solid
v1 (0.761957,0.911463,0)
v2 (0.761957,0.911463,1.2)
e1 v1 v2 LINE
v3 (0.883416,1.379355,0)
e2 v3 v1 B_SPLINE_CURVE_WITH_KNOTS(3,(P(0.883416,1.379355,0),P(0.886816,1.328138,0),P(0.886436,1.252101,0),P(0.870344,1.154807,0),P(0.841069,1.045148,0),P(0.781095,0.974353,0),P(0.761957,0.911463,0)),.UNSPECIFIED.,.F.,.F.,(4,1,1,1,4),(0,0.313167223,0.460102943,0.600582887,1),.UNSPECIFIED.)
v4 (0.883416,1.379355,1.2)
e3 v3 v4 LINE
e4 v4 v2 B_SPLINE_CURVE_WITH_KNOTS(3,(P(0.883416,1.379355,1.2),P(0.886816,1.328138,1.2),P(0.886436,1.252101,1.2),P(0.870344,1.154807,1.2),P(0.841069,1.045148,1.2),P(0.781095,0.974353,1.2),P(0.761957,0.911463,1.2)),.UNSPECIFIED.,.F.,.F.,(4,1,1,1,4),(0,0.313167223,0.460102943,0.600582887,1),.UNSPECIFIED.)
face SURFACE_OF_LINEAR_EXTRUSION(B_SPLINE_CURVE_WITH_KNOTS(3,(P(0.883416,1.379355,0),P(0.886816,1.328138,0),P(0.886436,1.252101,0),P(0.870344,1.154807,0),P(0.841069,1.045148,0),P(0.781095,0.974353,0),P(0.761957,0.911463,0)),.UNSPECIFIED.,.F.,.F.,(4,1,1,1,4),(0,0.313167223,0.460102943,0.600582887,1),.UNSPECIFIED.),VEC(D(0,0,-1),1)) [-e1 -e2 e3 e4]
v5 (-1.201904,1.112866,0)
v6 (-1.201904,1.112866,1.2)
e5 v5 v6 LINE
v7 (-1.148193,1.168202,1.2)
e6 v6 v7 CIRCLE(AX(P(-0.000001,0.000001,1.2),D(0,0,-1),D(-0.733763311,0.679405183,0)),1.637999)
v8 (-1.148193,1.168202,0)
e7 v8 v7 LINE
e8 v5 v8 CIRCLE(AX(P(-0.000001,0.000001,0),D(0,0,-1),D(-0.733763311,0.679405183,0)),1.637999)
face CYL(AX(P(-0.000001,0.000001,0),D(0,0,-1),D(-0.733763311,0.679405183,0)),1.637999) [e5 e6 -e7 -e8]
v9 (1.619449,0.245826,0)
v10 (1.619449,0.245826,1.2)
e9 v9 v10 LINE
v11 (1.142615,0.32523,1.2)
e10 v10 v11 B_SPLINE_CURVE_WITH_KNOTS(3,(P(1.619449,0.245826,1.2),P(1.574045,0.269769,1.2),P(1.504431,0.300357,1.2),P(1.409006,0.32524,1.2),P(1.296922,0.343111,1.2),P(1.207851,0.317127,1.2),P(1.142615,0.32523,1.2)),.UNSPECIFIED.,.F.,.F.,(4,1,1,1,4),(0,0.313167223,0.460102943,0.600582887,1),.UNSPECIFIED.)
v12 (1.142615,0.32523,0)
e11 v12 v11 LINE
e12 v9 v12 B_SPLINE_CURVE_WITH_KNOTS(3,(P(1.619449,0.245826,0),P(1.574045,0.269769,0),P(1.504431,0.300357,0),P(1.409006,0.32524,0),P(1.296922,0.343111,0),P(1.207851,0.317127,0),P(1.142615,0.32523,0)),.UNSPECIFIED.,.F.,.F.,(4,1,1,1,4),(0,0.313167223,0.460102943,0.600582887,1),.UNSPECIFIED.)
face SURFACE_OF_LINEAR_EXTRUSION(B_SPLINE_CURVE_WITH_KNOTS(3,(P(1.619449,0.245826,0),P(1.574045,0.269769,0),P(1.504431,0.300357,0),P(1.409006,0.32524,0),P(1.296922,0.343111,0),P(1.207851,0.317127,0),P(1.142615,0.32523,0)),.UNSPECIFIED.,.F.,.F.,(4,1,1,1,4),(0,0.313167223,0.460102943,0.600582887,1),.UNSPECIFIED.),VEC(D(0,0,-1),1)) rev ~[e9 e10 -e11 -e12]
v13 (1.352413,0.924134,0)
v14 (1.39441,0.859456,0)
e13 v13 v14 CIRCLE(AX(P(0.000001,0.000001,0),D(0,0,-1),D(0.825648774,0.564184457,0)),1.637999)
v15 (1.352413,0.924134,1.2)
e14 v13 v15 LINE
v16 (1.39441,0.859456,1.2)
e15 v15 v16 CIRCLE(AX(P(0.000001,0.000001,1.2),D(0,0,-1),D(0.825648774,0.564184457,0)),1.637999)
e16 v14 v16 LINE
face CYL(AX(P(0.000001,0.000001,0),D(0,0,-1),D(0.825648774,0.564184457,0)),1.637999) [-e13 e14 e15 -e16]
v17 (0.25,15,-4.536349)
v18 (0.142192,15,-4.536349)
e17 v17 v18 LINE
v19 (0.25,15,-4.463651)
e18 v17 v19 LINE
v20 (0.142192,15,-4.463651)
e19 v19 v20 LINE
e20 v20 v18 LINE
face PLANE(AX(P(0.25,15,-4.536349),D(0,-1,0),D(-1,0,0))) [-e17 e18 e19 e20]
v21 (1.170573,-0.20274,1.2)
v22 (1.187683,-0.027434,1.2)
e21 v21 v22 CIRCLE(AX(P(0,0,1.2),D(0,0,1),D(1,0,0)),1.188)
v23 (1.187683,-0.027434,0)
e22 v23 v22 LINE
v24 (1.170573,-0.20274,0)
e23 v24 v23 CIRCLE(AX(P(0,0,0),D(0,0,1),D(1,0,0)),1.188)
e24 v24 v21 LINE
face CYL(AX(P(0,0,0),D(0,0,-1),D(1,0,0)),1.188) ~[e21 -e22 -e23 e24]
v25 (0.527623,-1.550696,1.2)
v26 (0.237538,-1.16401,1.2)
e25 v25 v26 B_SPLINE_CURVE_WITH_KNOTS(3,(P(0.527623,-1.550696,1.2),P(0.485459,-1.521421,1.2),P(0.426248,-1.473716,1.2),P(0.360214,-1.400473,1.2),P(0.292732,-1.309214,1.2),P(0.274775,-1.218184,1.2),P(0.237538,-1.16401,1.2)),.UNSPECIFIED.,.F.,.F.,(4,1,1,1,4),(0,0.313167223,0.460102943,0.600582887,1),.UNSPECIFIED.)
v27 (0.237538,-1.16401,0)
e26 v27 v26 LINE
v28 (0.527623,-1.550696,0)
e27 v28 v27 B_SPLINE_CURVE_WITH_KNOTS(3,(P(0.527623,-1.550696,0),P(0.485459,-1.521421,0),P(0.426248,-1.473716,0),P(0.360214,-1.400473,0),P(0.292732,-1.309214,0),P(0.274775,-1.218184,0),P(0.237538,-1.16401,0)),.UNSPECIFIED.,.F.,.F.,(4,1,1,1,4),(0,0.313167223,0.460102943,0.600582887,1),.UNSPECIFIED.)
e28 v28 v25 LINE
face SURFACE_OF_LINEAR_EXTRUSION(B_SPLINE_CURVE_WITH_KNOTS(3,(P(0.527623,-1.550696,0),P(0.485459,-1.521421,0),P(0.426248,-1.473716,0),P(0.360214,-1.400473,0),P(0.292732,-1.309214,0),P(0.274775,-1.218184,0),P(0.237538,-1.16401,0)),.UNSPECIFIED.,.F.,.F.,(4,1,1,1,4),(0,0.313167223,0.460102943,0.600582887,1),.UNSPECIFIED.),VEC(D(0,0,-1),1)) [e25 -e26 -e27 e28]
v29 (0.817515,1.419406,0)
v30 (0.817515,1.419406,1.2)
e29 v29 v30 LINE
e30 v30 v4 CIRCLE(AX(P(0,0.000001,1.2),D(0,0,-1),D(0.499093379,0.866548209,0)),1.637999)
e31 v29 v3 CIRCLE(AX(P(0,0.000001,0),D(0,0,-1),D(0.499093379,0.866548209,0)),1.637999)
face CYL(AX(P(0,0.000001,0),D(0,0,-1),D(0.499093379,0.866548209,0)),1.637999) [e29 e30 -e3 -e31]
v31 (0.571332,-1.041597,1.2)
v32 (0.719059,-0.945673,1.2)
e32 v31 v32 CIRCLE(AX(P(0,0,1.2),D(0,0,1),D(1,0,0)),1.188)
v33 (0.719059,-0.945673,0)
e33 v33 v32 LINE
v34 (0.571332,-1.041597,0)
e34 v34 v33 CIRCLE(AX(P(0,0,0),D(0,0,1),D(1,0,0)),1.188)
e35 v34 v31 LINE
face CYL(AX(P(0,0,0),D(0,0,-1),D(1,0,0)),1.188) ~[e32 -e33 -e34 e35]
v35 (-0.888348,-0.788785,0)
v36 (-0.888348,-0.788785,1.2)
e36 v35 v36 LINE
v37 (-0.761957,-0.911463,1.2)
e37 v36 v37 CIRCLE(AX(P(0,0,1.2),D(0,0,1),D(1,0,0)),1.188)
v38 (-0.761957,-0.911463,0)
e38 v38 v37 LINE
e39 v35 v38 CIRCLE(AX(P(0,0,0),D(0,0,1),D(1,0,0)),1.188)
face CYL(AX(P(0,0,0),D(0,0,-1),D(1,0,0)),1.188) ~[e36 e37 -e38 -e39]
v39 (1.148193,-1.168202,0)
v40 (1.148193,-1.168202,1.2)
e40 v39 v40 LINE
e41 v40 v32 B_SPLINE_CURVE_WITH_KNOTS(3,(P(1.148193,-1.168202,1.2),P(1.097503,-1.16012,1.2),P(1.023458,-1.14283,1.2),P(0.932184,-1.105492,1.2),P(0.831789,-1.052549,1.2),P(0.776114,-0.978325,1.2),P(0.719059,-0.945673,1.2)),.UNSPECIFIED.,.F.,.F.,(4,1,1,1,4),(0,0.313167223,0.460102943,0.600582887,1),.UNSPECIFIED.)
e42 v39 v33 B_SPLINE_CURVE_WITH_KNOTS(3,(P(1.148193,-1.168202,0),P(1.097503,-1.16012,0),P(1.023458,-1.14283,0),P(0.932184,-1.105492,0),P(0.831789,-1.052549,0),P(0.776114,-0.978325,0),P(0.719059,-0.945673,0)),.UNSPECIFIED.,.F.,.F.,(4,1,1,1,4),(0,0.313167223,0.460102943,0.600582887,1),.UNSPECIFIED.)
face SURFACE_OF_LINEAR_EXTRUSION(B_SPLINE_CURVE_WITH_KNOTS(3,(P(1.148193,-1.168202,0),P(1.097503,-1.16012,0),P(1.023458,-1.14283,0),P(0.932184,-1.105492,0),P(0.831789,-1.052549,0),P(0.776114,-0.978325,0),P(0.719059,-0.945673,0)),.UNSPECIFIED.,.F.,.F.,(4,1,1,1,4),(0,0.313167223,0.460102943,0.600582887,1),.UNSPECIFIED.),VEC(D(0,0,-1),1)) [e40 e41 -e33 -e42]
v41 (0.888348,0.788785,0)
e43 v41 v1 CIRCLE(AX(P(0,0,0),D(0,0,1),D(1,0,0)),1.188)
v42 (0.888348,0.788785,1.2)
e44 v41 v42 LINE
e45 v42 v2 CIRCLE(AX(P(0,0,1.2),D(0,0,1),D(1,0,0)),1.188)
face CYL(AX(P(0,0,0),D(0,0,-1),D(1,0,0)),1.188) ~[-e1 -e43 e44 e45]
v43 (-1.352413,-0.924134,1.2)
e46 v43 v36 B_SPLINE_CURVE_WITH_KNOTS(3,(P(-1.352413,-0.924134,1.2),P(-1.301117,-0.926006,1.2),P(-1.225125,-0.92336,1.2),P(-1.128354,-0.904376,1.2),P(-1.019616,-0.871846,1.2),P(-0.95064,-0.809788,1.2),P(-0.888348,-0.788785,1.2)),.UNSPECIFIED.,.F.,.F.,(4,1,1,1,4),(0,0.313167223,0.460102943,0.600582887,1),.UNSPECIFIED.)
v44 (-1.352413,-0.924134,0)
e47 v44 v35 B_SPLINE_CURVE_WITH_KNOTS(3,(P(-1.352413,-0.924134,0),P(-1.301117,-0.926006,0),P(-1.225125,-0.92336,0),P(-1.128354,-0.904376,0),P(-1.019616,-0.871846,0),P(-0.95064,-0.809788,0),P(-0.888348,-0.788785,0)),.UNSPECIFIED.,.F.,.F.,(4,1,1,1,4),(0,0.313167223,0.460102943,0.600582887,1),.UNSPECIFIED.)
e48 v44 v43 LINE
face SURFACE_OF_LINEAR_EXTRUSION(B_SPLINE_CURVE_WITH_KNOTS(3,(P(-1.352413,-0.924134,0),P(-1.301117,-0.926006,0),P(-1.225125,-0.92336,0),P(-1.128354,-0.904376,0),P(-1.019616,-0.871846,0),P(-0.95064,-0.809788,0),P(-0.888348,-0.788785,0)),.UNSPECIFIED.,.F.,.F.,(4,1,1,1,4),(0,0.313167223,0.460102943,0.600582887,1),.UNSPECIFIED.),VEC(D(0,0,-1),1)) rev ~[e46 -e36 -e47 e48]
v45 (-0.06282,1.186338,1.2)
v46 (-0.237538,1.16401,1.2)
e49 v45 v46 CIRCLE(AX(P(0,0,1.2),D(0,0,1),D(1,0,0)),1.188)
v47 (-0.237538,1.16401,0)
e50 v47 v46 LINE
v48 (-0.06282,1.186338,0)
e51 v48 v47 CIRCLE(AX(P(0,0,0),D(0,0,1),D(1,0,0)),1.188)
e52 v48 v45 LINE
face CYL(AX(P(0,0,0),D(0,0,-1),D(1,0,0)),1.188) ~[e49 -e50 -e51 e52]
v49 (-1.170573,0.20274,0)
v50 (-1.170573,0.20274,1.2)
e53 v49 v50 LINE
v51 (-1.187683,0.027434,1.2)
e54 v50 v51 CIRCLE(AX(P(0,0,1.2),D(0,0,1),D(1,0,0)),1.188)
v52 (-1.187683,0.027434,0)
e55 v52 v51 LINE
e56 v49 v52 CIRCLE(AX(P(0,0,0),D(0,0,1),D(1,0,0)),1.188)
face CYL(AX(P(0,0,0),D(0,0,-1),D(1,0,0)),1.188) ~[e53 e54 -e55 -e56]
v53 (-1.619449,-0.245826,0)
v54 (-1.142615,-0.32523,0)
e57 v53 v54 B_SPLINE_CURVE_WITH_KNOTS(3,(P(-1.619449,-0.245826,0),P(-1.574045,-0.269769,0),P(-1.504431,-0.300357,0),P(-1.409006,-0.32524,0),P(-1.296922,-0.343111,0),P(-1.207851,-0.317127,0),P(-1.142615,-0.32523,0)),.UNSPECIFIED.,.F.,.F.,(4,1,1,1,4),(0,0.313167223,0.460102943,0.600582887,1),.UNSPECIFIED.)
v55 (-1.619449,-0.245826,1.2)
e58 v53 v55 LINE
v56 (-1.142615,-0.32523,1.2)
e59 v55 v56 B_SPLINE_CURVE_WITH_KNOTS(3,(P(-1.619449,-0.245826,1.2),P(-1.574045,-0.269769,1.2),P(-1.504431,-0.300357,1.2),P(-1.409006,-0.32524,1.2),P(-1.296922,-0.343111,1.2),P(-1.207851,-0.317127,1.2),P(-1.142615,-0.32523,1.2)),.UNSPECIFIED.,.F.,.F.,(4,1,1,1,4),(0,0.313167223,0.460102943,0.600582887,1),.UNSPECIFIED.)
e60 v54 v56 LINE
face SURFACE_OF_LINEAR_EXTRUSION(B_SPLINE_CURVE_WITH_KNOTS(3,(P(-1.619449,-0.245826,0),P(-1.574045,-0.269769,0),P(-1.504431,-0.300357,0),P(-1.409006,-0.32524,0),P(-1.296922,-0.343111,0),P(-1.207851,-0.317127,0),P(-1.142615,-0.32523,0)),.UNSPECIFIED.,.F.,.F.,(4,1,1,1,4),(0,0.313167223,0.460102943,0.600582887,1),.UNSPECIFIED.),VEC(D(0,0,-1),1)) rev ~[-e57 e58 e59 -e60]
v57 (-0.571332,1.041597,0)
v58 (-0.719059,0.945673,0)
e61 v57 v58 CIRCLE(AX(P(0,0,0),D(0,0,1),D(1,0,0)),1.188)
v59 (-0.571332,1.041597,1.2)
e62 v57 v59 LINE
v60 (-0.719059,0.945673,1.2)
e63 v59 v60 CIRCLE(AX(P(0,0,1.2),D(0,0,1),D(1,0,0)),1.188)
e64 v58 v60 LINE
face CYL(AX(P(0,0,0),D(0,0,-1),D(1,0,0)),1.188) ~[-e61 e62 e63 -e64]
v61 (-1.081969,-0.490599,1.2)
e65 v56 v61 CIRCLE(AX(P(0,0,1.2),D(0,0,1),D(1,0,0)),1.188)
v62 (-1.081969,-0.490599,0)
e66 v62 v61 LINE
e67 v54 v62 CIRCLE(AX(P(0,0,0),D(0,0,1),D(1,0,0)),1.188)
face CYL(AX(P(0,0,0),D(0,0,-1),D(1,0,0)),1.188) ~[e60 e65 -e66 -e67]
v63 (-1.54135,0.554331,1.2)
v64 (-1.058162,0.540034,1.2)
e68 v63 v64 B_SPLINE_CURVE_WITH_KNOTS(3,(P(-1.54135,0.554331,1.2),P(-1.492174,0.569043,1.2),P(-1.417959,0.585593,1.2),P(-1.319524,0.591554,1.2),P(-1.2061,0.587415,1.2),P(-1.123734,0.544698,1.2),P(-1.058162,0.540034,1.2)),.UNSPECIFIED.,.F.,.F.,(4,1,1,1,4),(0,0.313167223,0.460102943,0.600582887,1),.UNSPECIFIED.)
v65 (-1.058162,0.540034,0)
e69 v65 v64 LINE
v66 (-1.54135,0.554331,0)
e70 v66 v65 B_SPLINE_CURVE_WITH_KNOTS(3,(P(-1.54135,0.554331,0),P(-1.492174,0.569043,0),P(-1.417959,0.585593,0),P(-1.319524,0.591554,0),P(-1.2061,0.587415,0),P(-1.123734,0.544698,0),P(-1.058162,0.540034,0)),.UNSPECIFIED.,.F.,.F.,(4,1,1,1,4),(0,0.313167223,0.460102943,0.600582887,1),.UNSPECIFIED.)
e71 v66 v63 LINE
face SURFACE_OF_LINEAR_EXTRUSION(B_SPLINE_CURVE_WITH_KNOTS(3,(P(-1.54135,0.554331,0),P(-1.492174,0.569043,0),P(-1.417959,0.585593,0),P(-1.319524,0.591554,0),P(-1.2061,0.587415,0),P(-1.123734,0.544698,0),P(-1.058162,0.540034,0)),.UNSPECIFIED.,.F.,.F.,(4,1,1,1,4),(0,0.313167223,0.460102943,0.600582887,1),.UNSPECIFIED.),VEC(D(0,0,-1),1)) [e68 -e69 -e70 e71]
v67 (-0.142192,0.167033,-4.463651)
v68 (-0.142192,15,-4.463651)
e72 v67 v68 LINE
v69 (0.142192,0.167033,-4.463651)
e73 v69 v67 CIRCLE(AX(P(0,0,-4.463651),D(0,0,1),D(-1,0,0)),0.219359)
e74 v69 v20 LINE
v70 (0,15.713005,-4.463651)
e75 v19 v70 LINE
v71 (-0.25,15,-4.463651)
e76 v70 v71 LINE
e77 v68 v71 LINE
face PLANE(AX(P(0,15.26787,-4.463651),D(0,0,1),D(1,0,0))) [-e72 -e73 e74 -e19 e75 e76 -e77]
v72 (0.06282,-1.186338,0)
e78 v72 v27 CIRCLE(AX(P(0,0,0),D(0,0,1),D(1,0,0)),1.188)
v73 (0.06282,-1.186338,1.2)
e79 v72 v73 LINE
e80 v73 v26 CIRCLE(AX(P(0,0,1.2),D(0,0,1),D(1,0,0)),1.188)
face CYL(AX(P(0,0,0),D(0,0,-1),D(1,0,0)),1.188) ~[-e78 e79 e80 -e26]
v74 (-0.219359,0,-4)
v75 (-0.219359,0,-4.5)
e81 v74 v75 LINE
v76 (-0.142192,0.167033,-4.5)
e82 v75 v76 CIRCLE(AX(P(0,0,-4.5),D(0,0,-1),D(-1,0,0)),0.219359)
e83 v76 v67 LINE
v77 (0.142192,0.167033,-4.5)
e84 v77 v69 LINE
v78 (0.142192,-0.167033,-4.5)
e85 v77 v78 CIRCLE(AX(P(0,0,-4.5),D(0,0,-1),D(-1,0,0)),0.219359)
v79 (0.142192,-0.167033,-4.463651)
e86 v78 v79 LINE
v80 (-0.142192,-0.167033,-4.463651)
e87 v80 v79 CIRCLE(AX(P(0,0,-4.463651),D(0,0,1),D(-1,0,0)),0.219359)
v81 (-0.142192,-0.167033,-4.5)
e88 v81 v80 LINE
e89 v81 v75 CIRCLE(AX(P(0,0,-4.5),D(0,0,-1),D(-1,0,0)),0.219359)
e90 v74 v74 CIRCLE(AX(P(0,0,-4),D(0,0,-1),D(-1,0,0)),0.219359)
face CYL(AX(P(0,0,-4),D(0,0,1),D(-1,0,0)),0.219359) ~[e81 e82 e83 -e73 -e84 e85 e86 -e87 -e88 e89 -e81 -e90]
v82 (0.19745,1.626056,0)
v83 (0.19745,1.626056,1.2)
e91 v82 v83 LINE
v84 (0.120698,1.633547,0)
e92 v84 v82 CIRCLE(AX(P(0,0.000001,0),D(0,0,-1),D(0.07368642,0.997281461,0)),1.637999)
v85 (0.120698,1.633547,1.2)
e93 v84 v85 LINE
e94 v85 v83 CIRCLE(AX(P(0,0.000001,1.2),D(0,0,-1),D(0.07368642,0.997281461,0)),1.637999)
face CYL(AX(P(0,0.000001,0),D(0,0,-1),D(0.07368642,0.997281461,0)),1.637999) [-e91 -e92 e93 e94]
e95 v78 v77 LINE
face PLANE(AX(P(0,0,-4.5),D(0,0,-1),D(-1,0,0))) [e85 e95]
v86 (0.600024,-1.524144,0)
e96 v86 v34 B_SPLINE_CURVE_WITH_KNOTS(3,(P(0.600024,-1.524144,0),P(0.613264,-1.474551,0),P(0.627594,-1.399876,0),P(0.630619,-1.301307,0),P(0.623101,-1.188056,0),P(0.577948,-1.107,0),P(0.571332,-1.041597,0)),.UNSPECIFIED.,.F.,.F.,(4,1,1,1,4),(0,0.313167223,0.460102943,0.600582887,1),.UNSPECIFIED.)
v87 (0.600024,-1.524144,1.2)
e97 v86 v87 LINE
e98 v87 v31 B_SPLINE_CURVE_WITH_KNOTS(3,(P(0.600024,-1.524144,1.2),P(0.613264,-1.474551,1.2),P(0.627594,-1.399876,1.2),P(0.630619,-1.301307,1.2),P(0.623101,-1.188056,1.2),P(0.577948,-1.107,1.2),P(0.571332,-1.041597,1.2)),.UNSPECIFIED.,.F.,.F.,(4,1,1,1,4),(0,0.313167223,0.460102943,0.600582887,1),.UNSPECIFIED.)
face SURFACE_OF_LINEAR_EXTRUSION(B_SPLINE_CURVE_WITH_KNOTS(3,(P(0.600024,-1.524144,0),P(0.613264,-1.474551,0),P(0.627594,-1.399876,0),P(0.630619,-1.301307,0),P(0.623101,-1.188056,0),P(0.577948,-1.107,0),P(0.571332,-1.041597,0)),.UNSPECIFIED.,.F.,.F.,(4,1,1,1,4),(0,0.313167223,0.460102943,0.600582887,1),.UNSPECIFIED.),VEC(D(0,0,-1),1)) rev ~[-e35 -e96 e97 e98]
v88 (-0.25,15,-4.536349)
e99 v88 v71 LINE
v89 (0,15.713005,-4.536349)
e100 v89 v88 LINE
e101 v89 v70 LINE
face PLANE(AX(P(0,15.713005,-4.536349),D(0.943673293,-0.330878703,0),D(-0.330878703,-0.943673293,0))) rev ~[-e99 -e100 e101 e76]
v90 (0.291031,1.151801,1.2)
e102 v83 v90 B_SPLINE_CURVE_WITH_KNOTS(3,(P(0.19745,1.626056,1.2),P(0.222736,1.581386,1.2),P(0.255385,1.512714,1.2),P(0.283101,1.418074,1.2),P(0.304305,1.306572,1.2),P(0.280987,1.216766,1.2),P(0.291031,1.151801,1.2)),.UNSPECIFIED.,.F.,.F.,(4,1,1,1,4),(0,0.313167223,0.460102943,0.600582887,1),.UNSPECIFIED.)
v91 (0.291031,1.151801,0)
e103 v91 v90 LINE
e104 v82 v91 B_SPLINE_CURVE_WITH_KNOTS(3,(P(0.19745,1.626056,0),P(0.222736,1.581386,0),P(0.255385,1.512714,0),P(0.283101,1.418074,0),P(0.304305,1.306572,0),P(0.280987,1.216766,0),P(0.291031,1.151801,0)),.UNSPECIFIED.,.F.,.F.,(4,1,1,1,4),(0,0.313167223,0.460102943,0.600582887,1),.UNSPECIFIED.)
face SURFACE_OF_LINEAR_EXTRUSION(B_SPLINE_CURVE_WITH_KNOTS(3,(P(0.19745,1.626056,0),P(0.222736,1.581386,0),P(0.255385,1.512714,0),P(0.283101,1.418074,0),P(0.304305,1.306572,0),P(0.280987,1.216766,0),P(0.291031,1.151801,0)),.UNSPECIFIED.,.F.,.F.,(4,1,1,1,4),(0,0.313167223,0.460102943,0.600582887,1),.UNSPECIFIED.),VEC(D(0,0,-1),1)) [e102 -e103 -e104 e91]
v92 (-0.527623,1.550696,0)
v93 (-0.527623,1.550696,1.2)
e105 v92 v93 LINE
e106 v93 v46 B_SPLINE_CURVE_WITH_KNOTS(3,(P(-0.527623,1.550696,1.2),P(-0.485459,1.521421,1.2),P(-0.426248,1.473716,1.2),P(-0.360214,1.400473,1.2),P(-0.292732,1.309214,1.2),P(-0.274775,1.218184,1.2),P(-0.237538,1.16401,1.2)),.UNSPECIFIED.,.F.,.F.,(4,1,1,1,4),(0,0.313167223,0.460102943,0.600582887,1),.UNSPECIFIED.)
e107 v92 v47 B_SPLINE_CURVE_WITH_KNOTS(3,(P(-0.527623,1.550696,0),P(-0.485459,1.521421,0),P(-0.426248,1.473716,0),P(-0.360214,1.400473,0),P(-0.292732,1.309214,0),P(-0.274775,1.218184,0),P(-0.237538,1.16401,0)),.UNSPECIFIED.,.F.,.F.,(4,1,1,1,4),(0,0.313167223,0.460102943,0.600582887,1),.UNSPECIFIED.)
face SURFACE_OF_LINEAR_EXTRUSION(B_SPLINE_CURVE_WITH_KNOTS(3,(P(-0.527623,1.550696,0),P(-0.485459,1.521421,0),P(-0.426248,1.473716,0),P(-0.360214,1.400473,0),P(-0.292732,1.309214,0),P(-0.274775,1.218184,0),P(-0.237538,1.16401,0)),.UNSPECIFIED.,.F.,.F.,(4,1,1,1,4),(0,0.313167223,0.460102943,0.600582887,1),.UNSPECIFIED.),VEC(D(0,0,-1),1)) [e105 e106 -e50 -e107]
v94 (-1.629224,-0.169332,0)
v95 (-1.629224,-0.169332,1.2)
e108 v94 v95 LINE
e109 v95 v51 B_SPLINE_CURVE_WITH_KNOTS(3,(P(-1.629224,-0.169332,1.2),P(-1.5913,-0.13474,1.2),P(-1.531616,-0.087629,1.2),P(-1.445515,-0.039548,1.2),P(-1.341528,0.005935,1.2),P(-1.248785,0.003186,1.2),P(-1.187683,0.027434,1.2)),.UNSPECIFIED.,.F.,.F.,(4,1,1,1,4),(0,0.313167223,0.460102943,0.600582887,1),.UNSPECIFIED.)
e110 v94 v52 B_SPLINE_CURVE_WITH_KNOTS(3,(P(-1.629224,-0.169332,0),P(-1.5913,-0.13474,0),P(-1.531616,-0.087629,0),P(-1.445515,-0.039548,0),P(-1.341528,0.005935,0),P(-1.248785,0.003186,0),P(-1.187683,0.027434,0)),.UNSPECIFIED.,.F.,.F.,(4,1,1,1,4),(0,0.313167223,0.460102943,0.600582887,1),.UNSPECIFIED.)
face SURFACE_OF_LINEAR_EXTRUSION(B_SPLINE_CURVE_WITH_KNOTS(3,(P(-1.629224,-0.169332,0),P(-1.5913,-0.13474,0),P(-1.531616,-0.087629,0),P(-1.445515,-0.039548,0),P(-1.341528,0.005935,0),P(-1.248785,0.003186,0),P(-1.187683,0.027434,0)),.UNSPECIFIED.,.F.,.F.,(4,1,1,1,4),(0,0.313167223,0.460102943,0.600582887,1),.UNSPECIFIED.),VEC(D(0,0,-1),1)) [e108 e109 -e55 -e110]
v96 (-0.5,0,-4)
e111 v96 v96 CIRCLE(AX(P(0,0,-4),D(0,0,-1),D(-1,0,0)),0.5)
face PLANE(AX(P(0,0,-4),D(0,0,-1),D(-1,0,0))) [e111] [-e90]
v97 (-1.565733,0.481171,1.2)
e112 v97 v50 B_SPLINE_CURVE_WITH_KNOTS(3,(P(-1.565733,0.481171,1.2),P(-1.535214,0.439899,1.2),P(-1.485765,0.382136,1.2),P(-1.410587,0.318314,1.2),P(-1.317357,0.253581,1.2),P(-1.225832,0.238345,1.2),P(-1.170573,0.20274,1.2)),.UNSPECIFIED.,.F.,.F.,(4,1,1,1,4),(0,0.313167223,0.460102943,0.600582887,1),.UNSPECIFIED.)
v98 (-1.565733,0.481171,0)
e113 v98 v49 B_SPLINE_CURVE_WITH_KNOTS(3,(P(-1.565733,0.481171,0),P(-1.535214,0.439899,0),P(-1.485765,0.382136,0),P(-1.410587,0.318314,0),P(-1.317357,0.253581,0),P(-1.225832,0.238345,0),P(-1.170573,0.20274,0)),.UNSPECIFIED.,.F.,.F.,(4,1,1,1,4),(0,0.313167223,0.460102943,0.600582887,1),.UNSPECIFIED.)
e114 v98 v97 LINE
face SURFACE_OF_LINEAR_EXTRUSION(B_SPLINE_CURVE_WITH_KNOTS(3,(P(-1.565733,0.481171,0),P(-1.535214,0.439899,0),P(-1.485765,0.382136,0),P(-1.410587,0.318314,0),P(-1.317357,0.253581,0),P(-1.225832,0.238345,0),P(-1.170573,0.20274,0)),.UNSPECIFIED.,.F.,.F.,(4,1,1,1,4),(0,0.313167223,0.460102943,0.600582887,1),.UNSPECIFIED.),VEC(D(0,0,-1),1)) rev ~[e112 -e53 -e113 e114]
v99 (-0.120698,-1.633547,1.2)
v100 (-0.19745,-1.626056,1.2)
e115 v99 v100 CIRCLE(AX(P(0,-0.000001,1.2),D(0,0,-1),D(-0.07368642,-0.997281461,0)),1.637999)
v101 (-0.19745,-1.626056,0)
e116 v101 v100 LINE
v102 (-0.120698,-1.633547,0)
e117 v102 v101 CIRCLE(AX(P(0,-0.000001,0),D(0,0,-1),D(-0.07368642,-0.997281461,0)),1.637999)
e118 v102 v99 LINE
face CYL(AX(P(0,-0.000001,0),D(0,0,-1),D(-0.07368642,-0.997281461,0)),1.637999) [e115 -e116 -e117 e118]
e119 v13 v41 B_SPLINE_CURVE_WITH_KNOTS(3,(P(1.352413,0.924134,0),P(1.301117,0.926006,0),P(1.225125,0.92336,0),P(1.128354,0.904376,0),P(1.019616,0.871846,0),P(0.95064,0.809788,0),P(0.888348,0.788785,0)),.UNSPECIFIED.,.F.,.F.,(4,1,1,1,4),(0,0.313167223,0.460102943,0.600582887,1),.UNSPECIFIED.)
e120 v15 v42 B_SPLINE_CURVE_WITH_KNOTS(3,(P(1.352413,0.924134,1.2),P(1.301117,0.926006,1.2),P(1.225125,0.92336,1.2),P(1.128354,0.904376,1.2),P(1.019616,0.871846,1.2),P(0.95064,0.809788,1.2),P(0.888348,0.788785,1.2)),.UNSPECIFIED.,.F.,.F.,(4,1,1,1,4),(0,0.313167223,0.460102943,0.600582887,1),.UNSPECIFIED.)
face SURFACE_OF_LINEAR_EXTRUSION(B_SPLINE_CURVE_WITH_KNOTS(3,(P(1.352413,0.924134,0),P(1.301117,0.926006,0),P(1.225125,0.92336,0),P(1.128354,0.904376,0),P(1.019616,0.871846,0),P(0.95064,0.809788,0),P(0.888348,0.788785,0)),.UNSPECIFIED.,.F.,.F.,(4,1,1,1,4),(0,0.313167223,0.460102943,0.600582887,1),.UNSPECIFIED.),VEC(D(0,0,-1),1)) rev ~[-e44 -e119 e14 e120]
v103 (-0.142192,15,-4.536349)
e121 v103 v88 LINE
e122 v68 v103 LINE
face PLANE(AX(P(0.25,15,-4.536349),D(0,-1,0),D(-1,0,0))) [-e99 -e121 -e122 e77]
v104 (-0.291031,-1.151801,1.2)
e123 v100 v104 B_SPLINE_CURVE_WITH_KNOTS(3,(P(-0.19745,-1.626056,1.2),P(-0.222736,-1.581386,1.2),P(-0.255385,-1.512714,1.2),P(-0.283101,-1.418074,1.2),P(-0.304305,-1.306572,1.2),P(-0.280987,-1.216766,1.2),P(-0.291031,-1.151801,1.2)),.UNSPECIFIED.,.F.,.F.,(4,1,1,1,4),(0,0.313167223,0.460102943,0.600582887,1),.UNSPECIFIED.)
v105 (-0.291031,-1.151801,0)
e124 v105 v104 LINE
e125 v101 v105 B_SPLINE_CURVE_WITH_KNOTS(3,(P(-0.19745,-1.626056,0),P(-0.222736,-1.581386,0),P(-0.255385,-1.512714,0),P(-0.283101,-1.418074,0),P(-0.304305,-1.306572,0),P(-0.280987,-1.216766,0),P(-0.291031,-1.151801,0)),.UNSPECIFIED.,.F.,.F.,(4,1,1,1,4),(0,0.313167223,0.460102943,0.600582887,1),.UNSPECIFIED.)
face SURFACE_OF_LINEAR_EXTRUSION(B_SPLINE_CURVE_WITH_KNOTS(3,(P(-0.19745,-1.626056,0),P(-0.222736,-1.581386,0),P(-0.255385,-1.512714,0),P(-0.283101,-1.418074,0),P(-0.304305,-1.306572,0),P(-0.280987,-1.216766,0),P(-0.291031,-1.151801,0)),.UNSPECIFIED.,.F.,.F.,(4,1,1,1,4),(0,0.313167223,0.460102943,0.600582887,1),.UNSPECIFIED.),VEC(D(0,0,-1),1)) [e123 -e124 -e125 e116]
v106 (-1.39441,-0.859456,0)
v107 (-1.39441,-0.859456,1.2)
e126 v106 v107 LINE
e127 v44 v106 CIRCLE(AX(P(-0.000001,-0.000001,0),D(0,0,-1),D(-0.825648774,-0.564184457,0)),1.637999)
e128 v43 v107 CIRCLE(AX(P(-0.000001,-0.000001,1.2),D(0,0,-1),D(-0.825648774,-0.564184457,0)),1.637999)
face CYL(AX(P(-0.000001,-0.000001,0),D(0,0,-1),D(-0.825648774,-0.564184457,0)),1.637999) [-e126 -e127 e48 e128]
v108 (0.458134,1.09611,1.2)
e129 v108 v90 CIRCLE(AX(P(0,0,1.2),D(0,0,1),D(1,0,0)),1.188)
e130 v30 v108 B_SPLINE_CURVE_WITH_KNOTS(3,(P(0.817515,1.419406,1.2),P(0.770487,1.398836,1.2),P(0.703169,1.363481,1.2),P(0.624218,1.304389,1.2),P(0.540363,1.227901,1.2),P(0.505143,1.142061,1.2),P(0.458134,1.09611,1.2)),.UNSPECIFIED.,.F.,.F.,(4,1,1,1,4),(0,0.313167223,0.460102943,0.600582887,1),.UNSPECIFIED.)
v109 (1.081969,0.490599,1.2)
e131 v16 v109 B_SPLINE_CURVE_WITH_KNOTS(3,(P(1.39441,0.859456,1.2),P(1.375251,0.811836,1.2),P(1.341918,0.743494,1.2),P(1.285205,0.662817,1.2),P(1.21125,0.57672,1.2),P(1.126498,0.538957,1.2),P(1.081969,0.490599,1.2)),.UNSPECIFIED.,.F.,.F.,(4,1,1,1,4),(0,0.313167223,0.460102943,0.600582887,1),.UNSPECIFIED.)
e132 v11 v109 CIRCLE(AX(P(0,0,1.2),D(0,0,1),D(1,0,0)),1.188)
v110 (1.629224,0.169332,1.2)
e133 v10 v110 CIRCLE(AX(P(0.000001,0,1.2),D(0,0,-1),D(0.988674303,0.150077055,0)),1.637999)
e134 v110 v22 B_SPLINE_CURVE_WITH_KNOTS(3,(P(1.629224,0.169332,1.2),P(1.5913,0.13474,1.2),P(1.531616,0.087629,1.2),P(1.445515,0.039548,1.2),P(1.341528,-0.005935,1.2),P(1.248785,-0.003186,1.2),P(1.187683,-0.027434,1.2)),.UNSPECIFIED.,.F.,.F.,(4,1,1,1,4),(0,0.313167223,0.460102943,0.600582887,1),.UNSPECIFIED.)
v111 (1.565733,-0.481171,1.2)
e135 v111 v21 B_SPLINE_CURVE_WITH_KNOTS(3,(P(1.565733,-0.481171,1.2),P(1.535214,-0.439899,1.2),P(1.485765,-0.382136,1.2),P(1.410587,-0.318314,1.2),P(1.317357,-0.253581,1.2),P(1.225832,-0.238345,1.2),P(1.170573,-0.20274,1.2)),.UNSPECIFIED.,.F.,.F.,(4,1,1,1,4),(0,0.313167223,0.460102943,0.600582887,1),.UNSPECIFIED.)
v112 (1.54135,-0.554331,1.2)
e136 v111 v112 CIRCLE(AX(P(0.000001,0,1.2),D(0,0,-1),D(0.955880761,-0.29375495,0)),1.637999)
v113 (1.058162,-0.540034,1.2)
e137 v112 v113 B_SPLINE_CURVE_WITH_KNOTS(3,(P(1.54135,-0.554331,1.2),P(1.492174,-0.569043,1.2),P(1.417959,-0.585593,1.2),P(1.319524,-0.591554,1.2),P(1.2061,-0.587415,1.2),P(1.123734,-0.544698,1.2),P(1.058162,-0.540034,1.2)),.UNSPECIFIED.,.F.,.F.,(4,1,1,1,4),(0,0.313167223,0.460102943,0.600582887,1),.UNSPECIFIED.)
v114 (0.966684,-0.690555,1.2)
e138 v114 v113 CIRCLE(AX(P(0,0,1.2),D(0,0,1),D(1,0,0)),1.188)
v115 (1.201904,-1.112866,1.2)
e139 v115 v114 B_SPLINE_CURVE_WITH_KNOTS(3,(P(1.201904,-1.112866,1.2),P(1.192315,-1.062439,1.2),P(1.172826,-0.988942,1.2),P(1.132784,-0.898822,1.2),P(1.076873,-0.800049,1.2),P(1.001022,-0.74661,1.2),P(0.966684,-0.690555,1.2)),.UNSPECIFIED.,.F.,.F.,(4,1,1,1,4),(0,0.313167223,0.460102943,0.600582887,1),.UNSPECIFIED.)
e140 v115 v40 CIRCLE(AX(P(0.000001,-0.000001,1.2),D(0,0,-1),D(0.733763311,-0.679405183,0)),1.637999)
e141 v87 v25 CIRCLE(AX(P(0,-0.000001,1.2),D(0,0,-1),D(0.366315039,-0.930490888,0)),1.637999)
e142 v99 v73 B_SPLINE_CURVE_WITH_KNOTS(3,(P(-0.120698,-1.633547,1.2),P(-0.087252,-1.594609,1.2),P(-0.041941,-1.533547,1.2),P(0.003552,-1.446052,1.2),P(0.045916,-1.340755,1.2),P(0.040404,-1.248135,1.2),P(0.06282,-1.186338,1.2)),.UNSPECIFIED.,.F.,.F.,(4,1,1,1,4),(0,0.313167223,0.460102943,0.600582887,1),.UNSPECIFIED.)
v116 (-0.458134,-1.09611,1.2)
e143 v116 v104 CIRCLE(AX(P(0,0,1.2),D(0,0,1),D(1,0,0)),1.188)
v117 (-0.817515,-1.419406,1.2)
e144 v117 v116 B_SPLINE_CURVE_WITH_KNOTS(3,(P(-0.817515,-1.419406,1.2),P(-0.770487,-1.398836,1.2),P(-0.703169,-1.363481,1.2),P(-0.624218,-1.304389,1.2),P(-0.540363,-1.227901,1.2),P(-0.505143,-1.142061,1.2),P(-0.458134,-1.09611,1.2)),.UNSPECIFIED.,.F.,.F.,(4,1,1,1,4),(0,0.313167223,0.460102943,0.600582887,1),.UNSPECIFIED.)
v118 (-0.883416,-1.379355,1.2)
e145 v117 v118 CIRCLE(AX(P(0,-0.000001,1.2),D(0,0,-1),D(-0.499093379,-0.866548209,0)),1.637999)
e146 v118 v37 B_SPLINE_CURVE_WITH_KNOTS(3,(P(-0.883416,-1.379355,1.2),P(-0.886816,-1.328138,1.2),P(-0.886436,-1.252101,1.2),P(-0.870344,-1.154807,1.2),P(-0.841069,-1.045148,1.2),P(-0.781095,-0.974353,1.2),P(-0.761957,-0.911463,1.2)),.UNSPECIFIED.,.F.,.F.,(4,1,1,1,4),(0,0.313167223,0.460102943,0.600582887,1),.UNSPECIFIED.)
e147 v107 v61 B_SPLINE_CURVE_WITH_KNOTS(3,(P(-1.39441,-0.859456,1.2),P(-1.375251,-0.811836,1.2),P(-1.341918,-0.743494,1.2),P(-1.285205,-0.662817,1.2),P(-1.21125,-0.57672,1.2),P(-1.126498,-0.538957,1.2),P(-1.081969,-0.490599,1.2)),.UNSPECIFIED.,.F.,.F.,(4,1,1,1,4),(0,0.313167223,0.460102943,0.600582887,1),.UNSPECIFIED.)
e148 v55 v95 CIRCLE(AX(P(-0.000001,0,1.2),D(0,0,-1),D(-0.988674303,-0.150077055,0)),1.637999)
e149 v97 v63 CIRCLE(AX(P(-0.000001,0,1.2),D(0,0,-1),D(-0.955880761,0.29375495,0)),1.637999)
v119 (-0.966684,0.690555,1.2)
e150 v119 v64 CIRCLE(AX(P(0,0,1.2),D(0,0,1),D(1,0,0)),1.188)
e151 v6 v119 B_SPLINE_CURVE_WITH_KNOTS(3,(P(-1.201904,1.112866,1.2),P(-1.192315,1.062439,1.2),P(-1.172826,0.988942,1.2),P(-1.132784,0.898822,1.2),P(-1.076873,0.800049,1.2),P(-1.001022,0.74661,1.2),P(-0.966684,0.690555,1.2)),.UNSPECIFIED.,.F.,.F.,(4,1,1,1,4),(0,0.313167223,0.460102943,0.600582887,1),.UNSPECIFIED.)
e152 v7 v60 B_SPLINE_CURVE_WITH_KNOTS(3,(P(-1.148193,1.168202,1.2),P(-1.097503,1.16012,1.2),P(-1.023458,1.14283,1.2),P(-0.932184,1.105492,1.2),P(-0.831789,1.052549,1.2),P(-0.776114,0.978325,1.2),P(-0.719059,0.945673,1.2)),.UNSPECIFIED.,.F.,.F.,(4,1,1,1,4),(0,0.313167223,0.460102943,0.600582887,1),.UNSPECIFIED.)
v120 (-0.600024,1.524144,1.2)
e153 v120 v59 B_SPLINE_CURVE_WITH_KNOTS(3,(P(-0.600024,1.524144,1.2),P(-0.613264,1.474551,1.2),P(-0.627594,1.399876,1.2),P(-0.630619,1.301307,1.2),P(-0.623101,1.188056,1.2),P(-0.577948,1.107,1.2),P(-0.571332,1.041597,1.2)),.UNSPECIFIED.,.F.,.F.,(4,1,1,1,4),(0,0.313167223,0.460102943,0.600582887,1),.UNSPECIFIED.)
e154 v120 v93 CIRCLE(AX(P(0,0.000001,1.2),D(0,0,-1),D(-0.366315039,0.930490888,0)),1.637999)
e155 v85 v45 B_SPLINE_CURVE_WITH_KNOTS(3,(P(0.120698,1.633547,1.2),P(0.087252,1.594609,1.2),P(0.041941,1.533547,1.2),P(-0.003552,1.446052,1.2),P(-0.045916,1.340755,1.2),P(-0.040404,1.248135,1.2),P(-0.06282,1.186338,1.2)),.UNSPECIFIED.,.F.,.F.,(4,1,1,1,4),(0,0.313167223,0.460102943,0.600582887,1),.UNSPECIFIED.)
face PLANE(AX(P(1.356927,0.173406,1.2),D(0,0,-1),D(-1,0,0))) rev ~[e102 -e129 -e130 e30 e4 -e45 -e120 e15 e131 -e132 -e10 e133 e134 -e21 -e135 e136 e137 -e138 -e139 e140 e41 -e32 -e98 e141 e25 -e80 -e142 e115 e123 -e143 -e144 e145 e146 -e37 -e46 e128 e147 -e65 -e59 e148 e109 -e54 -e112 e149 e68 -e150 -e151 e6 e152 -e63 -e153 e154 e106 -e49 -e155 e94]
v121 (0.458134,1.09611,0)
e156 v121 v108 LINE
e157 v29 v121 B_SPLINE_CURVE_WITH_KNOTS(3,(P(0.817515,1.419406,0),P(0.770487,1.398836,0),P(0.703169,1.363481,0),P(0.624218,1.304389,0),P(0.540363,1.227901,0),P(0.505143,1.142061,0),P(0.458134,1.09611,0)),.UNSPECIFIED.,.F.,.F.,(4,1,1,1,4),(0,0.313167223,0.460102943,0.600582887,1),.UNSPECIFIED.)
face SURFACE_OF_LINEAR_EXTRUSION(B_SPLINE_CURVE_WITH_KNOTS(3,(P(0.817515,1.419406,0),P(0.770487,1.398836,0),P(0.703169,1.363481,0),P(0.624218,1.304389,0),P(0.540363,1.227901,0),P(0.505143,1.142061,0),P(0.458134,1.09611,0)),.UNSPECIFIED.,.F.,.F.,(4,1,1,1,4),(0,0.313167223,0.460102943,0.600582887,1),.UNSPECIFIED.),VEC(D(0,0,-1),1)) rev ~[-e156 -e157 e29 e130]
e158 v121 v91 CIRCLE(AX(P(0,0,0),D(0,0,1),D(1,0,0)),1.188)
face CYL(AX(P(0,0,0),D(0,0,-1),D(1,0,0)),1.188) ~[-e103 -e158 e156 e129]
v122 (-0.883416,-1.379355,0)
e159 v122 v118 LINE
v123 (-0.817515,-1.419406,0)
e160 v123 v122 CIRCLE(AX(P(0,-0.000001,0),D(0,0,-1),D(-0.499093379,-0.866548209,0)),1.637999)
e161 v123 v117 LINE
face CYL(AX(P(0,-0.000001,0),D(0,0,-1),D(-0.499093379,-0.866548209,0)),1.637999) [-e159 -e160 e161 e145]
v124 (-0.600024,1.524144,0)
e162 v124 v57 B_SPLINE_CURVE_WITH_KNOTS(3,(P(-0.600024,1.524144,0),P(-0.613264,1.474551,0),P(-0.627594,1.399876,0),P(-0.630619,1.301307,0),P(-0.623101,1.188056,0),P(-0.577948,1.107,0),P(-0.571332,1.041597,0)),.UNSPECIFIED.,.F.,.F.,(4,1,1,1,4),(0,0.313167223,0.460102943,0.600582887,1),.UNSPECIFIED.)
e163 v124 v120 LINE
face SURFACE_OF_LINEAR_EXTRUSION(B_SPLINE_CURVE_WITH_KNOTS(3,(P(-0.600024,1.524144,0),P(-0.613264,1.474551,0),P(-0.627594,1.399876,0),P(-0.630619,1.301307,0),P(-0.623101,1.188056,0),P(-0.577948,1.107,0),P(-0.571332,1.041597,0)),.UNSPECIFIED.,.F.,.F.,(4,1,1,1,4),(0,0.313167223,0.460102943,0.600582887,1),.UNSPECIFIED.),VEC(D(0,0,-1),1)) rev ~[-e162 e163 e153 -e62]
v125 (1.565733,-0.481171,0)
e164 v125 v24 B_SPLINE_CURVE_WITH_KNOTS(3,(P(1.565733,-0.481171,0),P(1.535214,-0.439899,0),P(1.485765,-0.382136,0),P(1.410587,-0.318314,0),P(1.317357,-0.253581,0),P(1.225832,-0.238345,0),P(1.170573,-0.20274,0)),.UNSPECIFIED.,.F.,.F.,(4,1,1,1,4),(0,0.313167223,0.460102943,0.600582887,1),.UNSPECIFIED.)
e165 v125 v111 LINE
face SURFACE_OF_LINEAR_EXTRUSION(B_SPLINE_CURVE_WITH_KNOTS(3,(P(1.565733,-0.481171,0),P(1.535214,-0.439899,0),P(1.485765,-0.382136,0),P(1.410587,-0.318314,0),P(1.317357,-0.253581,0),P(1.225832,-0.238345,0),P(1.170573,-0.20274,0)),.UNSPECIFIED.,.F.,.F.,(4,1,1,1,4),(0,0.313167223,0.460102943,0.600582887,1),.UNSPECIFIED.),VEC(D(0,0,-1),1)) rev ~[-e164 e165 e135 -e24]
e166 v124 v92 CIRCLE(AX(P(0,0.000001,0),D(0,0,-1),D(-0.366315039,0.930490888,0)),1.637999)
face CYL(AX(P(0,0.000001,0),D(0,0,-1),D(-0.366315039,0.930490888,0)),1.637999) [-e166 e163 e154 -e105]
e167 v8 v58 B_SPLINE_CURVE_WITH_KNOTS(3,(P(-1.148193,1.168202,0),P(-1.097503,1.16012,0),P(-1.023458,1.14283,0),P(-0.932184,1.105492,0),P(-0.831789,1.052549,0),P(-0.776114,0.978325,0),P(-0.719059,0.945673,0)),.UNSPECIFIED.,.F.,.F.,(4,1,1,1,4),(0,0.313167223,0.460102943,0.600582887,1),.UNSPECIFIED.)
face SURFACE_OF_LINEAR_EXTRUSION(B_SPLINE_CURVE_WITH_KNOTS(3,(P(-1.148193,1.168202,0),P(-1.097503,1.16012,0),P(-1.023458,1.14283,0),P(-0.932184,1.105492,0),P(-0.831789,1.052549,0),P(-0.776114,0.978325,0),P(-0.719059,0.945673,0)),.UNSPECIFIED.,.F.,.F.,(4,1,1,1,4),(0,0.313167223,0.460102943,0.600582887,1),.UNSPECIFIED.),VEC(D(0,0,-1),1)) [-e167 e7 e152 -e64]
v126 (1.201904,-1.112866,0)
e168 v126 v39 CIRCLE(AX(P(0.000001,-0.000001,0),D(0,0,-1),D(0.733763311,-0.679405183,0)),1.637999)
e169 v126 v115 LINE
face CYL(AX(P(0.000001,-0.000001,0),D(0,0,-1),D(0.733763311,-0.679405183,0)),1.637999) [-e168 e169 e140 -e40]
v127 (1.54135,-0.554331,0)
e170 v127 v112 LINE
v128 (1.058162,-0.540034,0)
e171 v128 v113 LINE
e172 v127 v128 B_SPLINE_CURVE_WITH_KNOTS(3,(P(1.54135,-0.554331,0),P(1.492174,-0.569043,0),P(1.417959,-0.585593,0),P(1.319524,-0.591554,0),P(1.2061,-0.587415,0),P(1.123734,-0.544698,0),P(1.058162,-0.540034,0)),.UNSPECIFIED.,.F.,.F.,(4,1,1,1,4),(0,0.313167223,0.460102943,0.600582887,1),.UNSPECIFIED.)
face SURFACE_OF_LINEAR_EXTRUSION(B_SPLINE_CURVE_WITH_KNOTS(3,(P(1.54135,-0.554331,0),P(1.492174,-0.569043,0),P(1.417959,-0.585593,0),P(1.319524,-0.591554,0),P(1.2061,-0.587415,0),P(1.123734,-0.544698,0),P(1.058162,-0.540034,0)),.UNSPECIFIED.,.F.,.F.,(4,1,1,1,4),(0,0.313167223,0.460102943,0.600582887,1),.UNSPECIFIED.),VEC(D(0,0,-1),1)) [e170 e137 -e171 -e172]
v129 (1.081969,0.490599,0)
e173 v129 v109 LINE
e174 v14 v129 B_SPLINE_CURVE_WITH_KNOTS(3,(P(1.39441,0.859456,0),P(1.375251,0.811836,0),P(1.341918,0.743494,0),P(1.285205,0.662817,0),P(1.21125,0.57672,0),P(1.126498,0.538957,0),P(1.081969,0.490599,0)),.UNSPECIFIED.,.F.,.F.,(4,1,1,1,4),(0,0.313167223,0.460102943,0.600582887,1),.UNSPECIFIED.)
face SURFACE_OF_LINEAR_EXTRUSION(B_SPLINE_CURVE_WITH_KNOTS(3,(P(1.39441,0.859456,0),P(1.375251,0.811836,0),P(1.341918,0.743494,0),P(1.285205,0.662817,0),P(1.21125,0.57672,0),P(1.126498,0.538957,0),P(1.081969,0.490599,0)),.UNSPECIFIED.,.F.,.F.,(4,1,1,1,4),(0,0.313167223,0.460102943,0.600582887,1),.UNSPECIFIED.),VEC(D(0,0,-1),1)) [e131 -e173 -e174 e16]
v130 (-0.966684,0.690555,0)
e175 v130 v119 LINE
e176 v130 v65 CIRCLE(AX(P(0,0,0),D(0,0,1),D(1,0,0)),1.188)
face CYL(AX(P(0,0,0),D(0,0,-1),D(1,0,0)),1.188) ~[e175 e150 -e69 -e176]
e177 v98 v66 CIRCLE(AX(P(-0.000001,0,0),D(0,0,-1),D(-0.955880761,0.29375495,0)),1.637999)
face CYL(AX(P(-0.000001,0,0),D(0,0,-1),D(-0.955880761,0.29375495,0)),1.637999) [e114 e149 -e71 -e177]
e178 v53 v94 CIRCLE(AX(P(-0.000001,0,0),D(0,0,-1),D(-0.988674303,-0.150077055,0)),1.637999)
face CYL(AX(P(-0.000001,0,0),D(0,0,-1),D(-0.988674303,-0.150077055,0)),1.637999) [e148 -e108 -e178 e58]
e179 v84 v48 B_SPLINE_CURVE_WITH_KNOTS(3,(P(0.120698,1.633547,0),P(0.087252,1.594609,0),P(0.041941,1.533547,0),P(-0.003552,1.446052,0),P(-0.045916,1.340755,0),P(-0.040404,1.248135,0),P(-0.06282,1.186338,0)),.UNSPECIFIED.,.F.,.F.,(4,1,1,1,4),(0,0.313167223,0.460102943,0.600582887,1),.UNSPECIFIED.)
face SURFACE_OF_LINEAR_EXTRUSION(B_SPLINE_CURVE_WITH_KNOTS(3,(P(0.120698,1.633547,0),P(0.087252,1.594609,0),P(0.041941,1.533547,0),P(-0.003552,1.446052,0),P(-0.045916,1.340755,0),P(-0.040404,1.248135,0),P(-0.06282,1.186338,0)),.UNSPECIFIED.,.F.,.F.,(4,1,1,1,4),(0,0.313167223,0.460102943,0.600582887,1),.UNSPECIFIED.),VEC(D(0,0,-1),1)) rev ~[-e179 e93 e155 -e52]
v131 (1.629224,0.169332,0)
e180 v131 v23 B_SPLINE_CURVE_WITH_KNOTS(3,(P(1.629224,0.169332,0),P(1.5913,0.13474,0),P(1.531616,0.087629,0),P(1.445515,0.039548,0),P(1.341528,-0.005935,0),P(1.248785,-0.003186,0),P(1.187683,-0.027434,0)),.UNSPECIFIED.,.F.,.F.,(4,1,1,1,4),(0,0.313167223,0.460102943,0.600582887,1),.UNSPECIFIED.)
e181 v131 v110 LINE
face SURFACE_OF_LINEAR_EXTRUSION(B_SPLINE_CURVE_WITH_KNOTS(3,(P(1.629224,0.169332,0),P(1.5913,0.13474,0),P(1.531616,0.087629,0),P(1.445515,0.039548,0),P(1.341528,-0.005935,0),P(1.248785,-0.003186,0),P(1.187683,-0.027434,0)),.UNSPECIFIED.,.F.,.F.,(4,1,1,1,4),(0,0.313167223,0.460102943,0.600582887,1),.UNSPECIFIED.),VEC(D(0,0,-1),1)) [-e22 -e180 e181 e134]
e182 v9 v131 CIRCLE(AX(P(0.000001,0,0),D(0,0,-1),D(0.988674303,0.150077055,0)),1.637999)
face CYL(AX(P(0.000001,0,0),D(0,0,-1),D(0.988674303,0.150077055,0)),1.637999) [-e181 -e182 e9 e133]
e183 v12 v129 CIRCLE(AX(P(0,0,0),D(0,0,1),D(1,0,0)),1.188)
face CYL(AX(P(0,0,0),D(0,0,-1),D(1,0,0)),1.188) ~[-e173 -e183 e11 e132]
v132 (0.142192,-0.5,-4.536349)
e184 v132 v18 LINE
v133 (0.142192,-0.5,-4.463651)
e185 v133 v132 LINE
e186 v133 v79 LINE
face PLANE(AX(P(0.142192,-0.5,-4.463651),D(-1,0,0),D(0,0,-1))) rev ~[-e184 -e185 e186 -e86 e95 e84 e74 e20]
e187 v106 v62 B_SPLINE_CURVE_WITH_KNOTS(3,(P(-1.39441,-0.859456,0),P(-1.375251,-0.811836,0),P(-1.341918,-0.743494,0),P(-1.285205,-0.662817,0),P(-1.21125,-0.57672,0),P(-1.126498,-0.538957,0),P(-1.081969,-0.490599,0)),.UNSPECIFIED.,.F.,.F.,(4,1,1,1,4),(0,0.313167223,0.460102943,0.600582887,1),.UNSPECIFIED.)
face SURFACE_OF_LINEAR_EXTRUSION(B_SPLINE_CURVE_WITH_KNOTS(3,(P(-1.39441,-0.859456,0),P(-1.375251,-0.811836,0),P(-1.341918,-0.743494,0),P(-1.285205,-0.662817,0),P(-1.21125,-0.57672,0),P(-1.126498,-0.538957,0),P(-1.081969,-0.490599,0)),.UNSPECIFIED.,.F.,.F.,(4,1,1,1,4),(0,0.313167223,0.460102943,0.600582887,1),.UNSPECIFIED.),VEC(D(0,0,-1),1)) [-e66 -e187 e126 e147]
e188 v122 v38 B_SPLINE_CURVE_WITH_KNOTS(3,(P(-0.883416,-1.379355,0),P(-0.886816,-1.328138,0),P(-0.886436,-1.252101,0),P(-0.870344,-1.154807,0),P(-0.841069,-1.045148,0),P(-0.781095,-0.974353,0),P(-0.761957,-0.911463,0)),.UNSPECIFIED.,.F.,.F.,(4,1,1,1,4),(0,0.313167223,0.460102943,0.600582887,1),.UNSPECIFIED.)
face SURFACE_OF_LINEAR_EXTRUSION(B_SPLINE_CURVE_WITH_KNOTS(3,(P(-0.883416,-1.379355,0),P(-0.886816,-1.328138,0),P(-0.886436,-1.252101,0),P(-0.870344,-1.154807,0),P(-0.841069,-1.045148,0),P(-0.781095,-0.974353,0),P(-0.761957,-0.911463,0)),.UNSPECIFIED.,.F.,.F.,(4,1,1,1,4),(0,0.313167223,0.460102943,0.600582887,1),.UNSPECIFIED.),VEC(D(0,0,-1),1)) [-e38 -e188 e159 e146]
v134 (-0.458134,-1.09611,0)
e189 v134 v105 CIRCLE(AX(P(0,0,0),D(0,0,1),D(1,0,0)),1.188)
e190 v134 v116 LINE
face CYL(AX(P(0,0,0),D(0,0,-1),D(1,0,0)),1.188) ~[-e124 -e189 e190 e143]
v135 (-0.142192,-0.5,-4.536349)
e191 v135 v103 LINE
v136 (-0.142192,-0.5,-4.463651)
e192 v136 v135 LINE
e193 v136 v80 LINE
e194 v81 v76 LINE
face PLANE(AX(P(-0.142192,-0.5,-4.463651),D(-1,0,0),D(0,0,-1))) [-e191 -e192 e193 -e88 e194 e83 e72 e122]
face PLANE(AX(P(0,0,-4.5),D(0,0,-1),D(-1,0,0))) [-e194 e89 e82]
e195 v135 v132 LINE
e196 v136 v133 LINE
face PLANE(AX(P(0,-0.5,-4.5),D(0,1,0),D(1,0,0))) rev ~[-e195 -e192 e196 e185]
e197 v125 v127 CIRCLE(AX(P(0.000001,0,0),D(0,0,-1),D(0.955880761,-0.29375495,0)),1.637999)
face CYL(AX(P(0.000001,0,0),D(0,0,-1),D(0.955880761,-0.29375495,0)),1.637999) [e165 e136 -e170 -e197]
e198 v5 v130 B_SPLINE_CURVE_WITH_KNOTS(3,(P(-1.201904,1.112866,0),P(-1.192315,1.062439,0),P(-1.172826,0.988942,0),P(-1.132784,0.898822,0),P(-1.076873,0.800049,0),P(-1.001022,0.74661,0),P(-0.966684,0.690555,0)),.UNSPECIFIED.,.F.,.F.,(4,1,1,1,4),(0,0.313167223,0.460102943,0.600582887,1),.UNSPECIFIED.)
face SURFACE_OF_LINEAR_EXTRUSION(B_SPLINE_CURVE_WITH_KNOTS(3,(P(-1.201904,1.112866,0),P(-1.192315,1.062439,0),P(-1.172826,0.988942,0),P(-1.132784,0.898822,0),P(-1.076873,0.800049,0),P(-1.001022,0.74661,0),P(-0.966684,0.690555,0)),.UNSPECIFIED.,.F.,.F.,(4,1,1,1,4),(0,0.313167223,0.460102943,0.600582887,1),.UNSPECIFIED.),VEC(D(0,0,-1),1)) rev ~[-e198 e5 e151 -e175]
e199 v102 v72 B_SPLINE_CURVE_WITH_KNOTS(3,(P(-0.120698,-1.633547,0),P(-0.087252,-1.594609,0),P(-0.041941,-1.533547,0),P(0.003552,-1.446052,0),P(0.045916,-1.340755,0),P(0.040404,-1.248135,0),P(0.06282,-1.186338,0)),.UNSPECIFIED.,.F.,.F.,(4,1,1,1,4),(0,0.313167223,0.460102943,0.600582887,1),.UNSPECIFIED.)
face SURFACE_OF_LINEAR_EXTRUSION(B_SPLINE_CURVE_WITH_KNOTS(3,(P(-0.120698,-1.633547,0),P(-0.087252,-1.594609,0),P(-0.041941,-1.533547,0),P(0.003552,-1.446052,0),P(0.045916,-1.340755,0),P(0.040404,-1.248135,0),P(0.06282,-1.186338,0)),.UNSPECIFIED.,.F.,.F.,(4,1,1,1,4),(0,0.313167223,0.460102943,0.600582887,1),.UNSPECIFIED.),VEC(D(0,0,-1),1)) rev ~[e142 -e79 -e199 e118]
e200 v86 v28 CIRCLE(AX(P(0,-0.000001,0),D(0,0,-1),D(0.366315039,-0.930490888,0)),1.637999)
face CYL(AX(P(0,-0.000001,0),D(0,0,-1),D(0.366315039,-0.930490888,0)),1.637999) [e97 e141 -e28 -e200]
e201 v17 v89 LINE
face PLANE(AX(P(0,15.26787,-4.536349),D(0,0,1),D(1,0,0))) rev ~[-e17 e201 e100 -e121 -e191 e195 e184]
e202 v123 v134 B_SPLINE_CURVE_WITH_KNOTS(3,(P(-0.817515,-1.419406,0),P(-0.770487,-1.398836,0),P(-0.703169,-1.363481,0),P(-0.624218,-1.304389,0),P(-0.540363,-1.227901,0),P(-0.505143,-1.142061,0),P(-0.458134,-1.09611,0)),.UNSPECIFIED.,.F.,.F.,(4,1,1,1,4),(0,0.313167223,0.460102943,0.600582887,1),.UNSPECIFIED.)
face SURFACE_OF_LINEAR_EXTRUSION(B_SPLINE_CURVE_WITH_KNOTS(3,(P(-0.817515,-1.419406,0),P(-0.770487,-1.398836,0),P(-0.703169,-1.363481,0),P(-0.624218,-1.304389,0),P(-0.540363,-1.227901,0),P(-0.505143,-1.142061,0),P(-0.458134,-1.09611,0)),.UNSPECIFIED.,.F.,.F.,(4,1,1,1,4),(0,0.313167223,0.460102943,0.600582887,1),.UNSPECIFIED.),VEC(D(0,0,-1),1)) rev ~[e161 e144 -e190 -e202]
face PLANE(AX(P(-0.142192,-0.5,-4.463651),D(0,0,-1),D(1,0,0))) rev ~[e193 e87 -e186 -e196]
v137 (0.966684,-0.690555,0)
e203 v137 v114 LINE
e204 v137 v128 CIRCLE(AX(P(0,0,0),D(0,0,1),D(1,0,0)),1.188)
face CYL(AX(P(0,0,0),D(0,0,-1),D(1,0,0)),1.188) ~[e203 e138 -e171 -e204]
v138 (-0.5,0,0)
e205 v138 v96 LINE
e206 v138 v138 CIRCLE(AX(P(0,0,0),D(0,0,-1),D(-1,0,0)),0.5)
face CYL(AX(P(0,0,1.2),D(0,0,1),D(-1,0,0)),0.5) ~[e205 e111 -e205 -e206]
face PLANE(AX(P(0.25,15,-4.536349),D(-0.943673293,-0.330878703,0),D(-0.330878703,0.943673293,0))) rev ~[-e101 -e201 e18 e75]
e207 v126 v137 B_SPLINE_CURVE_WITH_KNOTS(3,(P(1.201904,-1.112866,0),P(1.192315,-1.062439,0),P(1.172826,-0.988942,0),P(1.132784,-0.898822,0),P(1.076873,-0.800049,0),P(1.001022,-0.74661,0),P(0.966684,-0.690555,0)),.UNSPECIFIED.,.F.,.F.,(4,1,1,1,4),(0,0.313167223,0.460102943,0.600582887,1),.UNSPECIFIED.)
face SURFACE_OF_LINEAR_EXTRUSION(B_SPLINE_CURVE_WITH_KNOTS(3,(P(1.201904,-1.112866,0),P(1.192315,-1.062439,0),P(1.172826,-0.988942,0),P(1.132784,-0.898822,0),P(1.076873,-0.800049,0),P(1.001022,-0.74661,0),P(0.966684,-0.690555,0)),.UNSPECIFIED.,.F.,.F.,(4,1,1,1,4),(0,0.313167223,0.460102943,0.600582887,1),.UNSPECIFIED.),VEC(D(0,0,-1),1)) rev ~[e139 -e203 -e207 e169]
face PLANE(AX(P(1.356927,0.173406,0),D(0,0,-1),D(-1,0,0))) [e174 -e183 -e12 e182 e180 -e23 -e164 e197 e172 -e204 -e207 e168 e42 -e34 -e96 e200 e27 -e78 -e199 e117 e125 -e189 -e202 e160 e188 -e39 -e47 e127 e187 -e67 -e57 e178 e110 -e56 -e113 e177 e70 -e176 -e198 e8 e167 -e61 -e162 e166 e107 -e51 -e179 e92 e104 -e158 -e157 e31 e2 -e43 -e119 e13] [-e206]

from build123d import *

# Parameters (mm, degrees)
SKETCH1_R                = 1.188
SKETCH1_R_2              = 0.5
BOSS_EXTRUDE1_DEPTH      = 1.2
BOSS_EXTRUDE2_DEPTH      = 1.2
CIRPATTERN1_COUNT        = 14
BOSS_EXTRUDE3_DEPTH      = 4
BOSS_EXTRUDE3_DEPTH_BACK = 1.2
SKETCH3_R                = 0.5
SKETCH4_R                = 0.219359104
BOSS_EXTRUDE4_DEPTH      = 0.5
BOSS_EXTRUDE5_DEPTH      = 15
BOSS_EXTRUDE5_DEPTH_BACK = 0.5
SKETCH5_W                = 0.284383346
SKETCH5_H                = 0.072697092
BOSS_EXTRUDE6_DEPTH      = 0.072697092


with BuildPart() as part:
    # Sketch1 → Boss-Extrude1 (new body)
    with BuildSketch(Plane.XY):
        Circle(SKETCH1_R)
        Circle(SKETCH1_R_2, mode=Mode.SUBTRACT)
    extrude(amount=BOSS_EXTRUDE1_DEPTH)

    # Sketch2 → Boss-Extrude2 (add)
    with BuildSketch(Plane.XY):
        with BuildLine():
            ThreePointArc((1.619448512, 0.245826193), (1.624786484, 0.207636419), (1.629223993, 0.169331571))
            add(Edge.make_bspline(
                [(1.629223993, 0.169331571), (1.591300465, 0.134739741), (1.531615848, 0.087628678), (1.445515367, 0.039548212), (1.341528029, -0.00593525), (1.248784579, -0.003185884), (1.187683187, -0.027434427)],
                knots=[0, 0, 0, 0, 0.313167223, 0.460102943, 0.600582887, 1, 1, 1, 1], degree=3))
            ThreePointArc((1.187683187, -0.027434427), (1.178416571, 0.150593446), (1.14261508, 0.325230348))
            add(Edge.make_bspline(
                [(1.619448512, 0.245826193), (1.574044618, 0.269769358), (1.504430652, 0.300356961), (1.409005971, 0.325239773), (1.296922361, 0.34311087), (1.207850842, 0.317126815), (1.14261508, 0.325230348)],
                knots=[0, 0, 0, 0, 0.313167223, 0.460102943, 0.600582887, 1, 1, 1, 1], degree=3))
        make_face()
    boss_extrude2 = extrude(amount=BOSS_EXTRUDE2_DEPTH)

    # CirPattern1: Boss-Extrude2 ×14 about axis
    cirpattern1_axis = Axis((0, 0, 1.2), (0, 0, -1))
    for i in range(1, CIRPATTERN1_COUNT):
        add(boss_extrude2.rotate(cirpattern1_axis, i * 360 / CIRPATTERN1_COUNT))

    # Sketch3 → Boss-Extrude3 (add, two sides: drawn at the far end of the back side and taken through both)
    with BuildSketch(Plane(origin=(0, 0, 0), x_dir=(-1, 0, 0), z_dir=(0, 0, -1)).offset(-BOSS_EXTRUDE3_DEPTH_BACK)):
        Circle(SKETCH3_R)
    extrude(amount=BOSS_EXTRUDE3_DEPTH + BOSS_EXTRUDE3_DEPTH_BACK)

    # Sketch4 → Boss-Extrude4 (add)
    with BuildSketch(Plane(origin=(0, 0, -4), x_dir=(-1, 0, 0), z_dir=(0, 0, -1))):
        Circle(SKETCH4_R)
    extrude(amount=BOSS_EXTRUDE4_DEPTH)

    # Sketch5 → Boss-Extrude5 (add, two sides: drawn at the far end of the back side and taken through both)
    with BuildSketch(Plane(origin=(0, 0, 0), x_dir=(1, 0, 0), z_dir=(0, 1, 0)).offset(-BOSS_EXTRUDE5_DEPTH_BACK)):
        with Locations((0, 4.5)):
            Rectangle(SKETCH5_W, SKETCH5_H)
    extrude(amount=BOSS_EXTRUDE5_DEPTH + BOSS_EXTRUDE5_DEPTH_BACK)

    # Sketch6 → Boss-Extrude6 (add)
    with BuildSketch(Plane(origin=(0, 0, -4.536348546), x_dir=(-1, 0, 0), z_dir=(0, 0, -1))):
        Polygon((0, 15), (-0.25, 15), (0, 15.713005465), (0.25, 15), align=None)
    extrude(amount=-BOSS_EXTRUDE6_DEPTH)


solid = part.part
